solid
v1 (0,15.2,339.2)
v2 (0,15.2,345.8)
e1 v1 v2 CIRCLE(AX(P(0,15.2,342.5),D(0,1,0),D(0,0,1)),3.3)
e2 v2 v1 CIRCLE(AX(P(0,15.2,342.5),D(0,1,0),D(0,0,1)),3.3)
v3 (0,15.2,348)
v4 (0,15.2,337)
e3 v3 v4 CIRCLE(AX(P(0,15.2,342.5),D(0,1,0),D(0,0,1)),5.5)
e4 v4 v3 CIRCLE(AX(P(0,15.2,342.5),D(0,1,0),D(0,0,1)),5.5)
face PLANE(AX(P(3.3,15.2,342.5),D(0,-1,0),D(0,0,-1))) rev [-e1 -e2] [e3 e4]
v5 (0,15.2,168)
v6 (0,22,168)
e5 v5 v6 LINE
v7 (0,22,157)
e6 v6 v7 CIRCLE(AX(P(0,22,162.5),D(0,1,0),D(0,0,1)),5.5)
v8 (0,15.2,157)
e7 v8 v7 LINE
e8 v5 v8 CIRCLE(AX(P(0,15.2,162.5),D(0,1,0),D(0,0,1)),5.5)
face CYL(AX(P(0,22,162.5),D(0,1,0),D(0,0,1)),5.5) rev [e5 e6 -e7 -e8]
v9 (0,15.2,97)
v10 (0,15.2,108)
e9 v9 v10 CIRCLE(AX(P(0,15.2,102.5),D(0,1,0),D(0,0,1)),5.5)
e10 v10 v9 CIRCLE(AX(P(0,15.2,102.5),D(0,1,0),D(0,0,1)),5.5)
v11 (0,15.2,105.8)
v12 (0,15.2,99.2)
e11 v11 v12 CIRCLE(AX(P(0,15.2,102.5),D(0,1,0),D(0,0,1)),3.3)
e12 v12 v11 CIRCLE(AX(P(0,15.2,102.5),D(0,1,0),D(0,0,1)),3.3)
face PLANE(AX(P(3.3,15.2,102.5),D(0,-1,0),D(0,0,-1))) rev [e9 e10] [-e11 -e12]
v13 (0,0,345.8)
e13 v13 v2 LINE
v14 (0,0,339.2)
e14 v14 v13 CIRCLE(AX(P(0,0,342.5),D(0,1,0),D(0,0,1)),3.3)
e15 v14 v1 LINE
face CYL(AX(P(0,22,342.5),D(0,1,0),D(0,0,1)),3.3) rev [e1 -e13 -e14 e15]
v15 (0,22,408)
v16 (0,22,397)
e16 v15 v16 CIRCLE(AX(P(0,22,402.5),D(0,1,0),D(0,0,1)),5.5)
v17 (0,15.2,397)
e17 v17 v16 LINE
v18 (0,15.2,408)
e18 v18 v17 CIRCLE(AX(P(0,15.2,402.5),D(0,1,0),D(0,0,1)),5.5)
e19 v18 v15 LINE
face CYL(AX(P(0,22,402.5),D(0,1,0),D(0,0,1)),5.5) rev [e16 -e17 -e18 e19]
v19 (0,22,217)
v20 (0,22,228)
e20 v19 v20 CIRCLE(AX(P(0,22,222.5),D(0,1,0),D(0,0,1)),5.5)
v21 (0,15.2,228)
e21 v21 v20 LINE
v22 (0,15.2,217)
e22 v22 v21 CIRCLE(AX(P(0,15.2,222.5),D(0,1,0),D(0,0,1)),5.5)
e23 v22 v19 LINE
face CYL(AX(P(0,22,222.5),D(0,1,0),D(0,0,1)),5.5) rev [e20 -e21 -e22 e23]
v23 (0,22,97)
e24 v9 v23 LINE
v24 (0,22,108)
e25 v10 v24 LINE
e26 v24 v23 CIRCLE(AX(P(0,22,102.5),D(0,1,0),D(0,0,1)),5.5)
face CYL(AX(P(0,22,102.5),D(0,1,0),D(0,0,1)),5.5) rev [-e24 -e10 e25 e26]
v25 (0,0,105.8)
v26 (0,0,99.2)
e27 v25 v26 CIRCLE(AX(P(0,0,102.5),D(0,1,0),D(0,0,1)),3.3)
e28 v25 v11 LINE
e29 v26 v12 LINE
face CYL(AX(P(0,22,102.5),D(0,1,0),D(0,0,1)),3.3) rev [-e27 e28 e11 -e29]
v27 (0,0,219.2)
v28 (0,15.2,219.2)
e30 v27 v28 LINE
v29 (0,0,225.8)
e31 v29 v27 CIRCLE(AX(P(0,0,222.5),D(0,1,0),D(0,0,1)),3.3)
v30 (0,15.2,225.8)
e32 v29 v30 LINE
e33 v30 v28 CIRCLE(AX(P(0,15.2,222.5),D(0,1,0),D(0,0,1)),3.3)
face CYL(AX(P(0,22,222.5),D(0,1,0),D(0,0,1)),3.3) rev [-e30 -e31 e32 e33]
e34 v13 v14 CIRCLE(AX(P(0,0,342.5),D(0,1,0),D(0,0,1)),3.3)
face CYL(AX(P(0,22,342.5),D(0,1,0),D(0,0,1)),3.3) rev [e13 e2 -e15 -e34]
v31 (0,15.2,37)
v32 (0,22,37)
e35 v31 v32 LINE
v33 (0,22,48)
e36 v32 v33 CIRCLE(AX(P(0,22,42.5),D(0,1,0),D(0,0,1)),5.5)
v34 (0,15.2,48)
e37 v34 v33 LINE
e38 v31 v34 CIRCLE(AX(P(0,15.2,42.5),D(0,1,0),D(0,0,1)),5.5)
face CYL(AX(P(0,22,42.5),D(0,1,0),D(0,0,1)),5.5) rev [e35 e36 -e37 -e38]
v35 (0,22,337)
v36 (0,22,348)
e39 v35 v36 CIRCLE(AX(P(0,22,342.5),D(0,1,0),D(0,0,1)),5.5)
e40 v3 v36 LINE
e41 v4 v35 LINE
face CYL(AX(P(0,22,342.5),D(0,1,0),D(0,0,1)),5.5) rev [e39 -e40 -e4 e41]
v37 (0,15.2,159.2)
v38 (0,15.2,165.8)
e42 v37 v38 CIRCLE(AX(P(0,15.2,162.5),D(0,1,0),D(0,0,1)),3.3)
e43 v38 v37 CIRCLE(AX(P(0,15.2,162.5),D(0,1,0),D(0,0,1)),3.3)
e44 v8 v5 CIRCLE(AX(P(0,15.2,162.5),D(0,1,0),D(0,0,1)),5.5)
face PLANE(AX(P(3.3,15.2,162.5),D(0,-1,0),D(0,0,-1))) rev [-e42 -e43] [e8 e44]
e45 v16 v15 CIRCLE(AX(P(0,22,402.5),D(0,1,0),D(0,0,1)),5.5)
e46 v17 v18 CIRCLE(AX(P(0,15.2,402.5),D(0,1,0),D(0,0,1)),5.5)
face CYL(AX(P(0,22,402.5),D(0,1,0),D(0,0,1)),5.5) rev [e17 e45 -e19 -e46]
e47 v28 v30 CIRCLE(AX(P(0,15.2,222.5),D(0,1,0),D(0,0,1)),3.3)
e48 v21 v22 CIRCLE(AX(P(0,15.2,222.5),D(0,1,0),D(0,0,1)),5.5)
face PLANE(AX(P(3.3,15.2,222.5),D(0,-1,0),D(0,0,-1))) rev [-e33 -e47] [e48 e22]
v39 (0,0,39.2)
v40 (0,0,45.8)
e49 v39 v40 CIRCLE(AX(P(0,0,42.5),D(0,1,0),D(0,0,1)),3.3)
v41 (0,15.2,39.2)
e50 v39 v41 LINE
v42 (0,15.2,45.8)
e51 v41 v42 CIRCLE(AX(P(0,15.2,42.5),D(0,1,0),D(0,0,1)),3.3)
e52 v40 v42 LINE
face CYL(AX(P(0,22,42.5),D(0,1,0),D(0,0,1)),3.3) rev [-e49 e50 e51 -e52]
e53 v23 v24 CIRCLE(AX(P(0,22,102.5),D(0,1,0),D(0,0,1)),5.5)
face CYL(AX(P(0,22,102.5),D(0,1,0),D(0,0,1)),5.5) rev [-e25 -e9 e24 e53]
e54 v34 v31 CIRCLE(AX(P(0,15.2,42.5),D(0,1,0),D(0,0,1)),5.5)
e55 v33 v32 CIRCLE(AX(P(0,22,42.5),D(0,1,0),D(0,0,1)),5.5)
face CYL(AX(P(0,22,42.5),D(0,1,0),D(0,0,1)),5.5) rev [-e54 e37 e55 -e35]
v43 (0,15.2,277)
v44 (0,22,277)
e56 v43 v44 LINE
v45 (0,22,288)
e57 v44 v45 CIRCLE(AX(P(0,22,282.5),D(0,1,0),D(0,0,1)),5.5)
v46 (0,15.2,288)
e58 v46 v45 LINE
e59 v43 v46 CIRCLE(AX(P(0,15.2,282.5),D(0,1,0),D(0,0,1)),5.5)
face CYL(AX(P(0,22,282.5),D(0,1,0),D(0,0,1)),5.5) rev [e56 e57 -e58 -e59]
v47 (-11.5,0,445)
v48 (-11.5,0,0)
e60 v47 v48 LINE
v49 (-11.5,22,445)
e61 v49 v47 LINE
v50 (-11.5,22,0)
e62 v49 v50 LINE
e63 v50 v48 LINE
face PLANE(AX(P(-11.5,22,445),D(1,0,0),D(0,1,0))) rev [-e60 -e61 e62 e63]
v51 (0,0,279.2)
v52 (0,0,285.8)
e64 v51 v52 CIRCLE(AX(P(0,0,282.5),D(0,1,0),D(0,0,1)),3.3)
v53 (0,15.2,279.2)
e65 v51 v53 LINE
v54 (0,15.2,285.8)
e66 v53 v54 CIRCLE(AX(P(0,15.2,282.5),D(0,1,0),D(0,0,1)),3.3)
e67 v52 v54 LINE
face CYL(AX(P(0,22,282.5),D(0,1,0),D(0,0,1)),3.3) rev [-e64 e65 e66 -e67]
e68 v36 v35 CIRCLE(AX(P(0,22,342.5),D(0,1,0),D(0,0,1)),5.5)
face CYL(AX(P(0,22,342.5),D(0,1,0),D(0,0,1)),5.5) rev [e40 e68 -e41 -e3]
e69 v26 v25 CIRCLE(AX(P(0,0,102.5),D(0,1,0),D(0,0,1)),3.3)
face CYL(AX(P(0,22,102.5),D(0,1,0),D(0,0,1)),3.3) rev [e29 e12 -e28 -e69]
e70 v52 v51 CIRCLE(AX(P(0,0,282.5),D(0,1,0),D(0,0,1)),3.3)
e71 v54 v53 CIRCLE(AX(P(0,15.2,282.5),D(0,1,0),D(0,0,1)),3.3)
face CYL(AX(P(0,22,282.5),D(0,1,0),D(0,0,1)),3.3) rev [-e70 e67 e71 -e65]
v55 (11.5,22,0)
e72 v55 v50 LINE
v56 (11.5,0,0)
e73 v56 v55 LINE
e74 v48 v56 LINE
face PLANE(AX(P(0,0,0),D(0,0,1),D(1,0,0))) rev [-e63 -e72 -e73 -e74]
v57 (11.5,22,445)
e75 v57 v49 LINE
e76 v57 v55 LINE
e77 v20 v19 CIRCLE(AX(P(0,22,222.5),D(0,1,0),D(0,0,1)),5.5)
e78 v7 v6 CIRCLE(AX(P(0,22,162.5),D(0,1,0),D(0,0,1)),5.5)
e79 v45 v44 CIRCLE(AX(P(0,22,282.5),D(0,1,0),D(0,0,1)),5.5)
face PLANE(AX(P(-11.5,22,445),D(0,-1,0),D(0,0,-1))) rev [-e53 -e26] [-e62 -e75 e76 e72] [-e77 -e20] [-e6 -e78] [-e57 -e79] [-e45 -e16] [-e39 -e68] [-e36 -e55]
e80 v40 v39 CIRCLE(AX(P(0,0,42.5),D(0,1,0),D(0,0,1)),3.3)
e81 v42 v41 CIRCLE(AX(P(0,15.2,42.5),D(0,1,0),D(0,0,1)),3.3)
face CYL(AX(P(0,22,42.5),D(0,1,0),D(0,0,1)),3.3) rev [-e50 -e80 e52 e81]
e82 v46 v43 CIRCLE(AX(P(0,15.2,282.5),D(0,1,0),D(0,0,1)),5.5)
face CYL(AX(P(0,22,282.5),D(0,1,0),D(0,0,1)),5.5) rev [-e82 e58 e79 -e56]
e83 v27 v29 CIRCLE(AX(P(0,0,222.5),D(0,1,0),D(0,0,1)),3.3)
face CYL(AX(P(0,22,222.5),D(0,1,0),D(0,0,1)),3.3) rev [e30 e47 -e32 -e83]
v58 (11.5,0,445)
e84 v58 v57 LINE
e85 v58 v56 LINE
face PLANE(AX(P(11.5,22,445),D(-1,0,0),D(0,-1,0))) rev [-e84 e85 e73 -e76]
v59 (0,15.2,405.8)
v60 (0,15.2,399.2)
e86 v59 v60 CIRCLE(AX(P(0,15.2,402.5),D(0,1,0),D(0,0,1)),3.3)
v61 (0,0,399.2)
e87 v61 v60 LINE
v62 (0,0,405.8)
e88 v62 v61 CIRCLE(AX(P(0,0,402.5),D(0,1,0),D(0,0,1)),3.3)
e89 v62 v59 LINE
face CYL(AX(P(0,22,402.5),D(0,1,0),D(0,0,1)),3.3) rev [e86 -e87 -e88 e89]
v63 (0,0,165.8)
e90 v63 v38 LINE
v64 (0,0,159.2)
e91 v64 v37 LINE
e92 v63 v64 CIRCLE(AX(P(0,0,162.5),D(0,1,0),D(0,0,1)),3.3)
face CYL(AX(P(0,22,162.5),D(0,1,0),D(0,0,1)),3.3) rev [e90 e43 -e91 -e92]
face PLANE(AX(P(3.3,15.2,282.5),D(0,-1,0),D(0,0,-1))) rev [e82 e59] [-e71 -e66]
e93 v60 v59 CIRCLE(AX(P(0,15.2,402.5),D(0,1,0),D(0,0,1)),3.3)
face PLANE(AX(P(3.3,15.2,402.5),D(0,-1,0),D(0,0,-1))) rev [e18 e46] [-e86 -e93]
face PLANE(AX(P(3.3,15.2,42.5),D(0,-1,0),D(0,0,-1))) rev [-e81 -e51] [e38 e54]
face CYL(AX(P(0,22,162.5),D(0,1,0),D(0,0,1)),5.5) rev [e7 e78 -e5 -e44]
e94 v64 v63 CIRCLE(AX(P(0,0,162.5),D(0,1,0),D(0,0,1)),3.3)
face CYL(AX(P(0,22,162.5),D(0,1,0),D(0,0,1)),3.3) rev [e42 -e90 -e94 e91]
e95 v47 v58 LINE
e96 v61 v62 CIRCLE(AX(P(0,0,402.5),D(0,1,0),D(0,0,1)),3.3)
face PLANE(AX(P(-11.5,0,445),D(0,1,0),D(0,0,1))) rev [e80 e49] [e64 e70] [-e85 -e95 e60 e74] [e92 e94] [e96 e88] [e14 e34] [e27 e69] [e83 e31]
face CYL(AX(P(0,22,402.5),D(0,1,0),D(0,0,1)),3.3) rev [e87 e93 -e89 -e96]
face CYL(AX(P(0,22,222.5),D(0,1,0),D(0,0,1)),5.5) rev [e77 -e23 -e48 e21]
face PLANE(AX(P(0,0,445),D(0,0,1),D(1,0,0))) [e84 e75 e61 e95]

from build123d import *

# Parameters (mm, degrees)
SKETCH_1_W                = 23
SKETCH_1_H                = 22
EXTRUDE_1_DEPTH           = 445
HOLE_WIZARD_1_D           = 6.6
HOLE_WIZARD_1_CBORE_D     = 11
HOLE_WIZARD_1_CBORE_DEPTH = 6.8
PATTERN_LINEAR_1_COUNT    = 8
PATTERN_LINEAR_1_PITCH    = 60


with BuildPart() as part:
    # 草图1 → 凸台-拉伸1 (new body)
    with BuildSketch(Plane.XY):
        with Locations((0, 11)):
            Rectangle(SKETCH_1_W, SKETCH_1_H)
    extrude(amount=EXTRUDE_1_DEPTH)

    # 打孔尺寸(%根据)内六角圆柱头螺钉的类型1 (through all)
    with Locations(Plane(origin=(0, 22, 0), x_dir=(1, 0, 0), z_dir=(0, 1, 0))):
        with Locations((0, -402.5)):
            hole_wizard_1 = CounterBoreHole(HOLE_WIZARD_1_D / 2, HOLE_WIZARD_1_CBORE_D / 2, HOLE_WIZARD_1_CBORE_DEPTH)

    # 阵列(线性)1: 打孔尺寸(%根据)内六角圆柱头螺钉的类型1 ×8
    with Locations(*[(0, 0, -i * PATTERN_LINEAR_1_PITCH) for i in range(1, PATTERN_LINEAR_1_COUNT)]):
        add(hole_wizard_1, mode=Mode.SUBTRACT)


solid = part.part
